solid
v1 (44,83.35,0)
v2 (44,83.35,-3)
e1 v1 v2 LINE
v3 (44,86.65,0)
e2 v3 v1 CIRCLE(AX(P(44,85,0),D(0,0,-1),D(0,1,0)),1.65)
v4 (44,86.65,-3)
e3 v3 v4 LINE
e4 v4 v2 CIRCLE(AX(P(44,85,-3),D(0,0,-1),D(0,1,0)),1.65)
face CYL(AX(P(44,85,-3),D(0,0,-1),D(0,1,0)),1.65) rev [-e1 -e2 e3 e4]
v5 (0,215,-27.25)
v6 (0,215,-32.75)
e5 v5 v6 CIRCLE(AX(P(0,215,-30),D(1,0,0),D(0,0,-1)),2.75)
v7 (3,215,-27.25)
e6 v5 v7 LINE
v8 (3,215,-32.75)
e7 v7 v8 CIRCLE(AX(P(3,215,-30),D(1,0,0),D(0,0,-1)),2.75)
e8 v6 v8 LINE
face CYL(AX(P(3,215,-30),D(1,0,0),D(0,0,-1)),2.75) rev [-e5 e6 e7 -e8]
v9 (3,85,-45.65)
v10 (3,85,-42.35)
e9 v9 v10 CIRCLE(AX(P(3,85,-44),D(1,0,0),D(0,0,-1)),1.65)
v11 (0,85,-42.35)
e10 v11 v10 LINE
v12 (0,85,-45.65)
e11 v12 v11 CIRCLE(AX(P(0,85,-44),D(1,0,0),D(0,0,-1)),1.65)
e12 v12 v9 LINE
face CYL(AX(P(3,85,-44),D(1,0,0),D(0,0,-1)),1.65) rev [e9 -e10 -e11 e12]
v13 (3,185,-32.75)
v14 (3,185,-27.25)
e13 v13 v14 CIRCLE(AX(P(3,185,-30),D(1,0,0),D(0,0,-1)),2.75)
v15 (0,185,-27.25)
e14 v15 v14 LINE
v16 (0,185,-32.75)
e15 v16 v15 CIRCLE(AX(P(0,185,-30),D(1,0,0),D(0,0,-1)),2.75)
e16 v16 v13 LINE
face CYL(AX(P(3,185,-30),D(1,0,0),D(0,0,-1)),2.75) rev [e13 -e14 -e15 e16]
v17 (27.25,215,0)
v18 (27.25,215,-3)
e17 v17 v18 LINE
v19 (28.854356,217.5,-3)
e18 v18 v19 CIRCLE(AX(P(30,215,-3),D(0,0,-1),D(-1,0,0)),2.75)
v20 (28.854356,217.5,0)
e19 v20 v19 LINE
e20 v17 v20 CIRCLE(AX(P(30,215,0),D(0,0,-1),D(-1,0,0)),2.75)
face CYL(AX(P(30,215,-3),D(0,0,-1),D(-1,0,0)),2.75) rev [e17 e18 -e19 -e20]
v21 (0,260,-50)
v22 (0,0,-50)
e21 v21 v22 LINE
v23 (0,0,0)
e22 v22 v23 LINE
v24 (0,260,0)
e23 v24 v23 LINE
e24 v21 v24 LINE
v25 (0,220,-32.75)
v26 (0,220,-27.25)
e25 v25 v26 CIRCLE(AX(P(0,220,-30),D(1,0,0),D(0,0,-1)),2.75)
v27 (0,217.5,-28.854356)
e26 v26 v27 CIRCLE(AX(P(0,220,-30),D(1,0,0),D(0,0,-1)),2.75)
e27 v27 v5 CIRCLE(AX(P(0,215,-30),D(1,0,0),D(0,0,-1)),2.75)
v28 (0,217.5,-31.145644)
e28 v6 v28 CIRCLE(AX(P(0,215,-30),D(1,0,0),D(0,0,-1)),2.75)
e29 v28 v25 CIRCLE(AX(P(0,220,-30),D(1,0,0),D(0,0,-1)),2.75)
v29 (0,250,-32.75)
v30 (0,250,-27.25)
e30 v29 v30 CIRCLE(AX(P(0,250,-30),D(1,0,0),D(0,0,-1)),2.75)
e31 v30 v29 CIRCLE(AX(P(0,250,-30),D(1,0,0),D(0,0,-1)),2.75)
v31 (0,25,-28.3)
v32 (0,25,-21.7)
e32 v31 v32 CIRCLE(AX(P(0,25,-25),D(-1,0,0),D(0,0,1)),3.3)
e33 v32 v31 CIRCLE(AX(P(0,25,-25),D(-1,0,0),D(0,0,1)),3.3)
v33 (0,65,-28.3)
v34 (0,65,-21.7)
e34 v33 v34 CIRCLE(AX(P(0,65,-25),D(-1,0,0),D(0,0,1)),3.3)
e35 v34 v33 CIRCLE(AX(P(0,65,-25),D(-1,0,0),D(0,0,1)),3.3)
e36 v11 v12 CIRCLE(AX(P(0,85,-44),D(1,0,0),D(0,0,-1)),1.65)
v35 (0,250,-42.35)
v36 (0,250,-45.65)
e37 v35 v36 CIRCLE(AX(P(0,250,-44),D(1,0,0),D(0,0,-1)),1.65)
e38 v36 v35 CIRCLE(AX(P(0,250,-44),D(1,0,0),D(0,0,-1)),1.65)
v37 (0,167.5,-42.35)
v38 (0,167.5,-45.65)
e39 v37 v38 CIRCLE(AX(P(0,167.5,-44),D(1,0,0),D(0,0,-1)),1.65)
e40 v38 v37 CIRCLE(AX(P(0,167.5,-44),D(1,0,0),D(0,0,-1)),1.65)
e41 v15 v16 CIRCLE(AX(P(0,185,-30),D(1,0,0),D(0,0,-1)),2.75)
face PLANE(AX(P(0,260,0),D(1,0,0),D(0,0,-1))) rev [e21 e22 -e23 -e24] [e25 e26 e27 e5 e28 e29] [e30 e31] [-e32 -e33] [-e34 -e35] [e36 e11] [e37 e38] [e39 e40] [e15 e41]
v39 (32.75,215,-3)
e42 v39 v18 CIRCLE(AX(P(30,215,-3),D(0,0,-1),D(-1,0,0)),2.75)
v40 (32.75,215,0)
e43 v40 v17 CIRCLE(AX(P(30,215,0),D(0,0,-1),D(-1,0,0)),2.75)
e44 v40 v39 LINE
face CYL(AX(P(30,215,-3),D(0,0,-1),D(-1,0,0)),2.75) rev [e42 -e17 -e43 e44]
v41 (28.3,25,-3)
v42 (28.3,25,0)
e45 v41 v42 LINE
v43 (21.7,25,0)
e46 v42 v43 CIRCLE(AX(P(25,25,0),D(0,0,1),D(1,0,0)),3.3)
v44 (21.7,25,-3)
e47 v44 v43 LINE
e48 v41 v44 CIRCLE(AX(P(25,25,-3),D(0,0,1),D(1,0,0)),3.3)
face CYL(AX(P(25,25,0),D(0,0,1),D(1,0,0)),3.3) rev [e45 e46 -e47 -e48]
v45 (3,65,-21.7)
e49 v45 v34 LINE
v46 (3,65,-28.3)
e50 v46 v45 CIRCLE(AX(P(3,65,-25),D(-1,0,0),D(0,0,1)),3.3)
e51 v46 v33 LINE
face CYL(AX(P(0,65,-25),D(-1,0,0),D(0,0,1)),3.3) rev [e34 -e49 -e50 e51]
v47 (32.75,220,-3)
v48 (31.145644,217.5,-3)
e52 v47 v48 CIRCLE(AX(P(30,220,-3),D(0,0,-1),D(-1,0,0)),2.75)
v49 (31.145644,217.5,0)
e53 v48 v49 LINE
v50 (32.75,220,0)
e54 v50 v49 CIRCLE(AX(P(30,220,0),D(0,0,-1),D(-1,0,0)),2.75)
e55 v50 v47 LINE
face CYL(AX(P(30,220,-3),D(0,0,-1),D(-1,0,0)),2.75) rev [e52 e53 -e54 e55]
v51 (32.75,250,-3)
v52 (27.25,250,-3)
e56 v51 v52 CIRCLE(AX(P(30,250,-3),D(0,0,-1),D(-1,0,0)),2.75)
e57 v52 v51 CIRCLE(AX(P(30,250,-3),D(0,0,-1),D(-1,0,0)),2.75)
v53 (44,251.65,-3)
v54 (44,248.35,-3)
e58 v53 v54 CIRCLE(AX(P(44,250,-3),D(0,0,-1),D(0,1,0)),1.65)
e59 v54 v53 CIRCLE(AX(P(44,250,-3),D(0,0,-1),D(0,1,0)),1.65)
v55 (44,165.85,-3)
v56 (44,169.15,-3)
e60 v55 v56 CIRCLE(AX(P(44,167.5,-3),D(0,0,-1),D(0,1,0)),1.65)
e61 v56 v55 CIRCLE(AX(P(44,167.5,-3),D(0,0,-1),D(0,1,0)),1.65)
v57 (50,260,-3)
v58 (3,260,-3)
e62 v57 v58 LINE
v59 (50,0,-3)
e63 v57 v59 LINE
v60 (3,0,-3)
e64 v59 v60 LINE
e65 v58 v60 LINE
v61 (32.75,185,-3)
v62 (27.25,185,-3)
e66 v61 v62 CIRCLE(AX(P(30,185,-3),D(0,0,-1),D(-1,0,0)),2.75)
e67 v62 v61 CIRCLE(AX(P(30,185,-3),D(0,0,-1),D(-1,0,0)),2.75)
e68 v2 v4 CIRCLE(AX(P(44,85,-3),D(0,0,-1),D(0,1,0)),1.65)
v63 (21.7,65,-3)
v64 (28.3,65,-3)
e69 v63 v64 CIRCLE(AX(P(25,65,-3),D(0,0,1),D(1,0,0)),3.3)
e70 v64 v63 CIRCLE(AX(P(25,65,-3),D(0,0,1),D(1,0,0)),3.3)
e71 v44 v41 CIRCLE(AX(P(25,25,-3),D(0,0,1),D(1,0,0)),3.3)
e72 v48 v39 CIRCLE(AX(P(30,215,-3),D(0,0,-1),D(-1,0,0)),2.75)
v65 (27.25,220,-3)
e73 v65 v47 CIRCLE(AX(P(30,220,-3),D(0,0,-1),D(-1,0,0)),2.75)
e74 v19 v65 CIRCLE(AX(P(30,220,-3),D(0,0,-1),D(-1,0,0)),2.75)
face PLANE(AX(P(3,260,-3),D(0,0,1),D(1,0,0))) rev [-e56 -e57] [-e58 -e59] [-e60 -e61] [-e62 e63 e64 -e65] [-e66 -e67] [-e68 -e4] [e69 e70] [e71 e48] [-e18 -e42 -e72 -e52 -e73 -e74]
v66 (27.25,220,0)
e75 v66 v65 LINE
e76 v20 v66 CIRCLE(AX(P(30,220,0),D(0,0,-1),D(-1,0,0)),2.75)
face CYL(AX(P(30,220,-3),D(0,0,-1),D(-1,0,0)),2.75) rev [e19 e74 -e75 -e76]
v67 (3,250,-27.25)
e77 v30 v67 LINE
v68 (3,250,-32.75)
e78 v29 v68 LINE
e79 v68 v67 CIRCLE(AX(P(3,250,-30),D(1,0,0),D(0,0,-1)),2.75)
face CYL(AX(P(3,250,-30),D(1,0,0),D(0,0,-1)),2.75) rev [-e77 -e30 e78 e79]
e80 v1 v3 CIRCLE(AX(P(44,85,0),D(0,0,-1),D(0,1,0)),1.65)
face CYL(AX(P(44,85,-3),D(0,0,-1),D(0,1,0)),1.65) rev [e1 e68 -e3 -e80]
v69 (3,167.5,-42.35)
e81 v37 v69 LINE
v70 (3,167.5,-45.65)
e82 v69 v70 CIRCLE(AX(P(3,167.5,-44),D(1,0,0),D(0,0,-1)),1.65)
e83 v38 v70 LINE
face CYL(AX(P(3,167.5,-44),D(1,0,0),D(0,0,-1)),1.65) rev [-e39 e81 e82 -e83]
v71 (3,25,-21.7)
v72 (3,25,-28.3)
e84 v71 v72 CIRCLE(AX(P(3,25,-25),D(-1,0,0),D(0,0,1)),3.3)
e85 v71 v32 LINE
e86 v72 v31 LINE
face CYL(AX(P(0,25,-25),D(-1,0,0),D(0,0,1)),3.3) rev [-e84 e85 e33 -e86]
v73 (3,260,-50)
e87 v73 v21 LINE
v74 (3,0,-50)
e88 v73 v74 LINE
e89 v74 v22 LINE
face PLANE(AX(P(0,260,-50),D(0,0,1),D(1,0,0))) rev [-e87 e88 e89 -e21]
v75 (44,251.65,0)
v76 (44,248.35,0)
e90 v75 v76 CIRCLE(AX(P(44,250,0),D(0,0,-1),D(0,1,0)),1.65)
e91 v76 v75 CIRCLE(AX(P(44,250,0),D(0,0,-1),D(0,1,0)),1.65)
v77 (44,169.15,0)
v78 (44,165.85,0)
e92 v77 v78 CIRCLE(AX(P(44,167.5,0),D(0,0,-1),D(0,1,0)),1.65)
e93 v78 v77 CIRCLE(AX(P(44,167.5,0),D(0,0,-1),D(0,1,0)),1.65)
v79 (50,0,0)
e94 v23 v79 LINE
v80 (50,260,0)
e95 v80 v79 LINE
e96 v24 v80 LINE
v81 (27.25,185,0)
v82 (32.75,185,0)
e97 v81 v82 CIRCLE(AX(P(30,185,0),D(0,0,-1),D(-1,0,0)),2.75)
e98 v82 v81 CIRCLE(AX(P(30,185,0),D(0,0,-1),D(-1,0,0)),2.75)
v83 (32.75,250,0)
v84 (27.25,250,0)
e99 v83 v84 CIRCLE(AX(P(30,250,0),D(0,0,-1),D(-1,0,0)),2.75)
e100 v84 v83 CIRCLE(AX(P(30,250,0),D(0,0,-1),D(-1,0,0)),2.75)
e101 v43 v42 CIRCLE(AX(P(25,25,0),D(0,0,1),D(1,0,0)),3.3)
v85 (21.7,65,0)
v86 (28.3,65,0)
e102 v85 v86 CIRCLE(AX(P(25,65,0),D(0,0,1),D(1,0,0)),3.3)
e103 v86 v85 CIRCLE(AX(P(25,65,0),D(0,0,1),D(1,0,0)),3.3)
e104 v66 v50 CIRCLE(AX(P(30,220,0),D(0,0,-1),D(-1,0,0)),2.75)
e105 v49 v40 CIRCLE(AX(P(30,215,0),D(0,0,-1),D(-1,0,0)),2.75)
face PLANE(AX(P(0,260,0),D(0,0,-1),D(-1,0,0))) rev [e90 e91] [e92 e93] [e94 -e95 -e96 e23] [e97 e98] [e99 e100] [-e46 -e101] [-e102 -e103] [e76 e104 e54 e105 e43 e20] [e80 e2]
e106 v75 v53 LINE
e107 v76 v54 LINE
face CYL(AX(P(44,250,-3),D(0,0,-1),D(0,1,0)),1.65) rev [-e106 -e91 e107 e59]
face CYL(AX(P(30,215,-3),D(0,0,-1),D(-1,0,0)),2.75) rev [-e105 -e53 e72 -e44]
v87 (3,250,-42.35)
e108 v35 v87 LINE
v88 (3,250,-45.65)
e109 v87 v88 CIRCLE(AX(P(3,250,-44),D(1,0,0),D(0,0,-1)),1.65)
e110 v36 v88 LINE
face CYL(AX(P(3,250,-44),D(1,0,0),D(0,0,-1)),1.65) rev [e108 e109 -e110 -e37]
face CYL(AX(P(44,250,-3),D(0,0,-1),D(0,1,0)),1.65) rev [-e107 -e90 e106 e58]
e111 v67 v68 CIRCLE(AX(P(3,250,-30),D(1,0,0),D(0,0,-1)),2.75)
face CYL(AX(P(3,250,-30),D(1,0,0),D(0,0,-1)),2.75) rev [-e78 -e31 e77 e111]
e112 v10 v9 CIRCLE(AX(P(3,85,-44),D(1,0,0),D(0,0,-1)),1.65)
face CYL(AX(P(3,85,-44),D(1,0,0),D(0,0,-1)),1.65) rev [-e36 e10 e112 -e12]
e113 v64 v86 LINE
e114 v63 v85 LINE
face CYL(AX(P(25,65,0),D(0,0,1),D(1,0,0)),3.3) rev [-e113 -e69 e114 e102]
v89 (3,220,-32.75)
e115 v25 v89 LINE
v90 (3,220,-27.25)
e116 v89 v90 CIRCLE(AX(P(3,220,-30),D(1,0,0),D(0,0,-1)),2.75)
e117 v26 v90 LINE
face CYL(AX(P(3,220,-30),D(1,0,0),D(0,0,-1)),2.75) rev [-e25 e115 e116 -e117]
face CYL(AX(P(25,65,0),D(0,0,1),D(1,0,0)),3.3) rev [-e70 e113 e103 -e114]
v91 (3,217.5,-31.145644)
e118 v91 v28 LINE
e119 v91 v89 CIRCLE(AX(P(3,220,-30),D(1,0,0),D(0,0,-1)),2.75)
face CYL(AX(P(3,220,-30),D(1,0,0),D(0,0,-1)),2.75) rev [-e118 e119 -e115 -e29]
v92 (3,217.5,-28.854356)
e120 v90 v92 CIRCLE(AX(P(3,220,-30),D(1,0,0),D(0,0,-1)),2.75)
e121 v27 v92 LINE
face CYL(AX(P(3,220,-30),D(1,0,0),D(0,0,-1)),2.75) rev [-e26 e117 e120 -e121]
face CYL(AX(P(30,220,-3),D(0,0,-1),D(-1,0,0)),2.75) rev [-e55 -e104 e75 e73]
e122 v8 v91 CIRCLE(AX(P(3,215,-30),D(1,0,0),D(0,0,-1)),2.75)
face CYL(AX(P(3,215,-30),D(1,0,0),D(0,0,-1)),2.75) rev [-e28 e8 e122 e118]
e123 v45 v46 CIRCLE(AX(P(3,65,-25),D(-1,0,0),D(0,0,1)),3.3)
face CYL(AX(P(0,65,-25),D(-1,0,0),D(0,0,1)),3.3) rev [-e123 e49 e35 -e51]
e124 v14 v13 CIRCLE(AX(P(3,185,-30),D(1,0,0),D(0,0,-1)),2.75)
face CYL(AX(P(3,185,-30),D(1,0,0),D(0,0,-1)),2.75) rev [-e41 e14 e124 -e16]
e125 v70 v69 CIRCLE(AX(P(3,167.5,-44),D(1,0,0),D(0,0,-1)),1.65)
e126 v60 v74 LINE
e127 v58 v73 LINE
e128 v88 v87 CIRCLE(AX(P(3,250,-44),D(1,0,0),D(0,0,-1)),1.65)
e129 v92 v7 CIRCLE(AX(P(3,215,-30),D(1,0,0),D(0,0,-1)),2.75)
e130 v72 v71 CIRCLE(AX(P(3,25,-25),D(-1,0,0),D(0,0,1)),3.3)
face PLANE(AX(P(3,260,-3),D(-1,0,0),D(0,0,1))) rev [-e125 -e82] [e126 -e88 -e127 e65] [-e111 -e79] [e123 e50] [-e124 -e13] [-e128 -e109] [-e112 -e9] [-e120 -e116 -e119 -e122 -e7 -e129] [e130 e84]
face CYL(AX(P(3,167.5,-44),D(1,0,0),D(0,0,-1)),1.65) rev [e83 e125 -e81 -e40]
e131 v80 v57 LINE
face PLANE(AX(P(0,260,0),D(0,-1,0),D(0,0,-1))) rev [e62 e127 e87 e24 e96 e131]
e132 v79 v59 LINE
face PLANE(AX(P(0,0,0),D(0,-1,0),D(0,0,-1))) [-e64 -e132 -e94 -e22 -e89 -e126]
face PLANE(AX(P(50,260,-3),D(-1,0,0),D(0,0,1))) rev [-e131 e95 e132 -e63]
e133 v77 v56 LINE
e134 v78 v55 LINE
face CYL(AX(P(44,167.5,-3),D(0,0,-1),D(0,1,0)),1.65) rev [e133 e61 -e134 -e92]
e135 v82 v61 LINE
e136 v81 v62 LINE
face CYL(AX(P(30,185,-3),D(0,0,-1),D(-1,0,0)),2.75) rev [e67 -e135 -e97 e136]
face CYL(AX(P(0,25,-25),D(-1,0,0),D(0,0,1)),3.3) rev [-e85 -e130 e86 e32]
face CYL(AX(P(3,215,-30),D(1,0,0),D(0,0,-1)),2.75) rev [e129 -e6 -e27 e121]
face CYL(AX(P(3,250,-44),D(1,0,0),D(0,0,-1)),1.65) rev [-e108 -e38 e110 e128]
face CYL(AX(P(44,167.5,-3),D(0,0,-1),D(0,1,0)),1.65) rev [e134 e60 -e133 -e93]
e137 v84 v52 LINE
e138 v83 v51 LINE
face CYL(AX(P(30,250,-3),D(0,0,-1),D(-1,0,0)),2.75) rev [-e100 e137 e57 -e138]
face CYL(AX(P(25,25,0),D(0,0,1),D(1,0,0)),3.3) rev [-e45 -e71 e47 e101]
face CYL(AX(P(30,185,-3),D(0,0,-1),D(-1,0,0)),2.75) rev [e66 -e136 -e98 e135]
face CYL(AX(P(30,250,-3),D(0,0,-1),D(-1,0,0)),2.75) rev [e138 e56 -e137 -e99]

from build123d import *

# Parameters (mm, degrees)
EXTRUDE_1_DEPTH    = 260
HOLE_WIZARD_M5_1_D = 5.5
HOLE_WIZARD_M5_2_D = 5.5
HOLE_WIZARD_M6_1_D = 6.6
HOLE_WIZARD_M6_2_D = 6.6
HOLE_WIZARD_M4_1_D = 3.3
HOLE_WIZARD_M4_2_D = 3.3


with BuildPart() as part:
    # 草图1 → 凸台-拉伸1 (new body)
    with BuildSketch(Plane(origin=(0, 0, 0), x_dir=(1, 0, 0), z_dir=(0, 1, 0))):
        Polygon((0, 0), (50, 0), (50, 3), (3, 3), (3, 50), (0, 50), align=None)
    extrude(amount=EXTRUDE_1_DEPTH)

    # M5 间隙孔1 (through all)
    with Locations(Plane(origin=(0, 0, -3), x_dir=(-1, 0, 0), z_dir=(0, 0, -1))):
        with Locations((-30, 250), (-30, 215), (-30, 220), (-30, 185)):
            Hole(HOLE_WIZARD_M5_1_D / 2)

    # M5 间隙孔2 (through all)
    with Locations(Plane(origin=(3, 0, 0), x_dir=(0, 0, -1), z_dir=(1, 0, 0))):
        with Locations((30, 220), (30, 185), (30, 250), (30, 215)):
            Hole(HOLE_WIZARD_M5_2_D / 2)

    # M6 间隙孔1 (through all)
    with Locations(Plane.XY):
        with Locations((25, 65), (25, 25)):
            Hole(HOLE_WIZARD_M6_1_D / 2)

    # M6 间隙孔2 (through all)
    with Locations(Plane.ZY):
        with Locations((-25, 65), (-25, 25)):
            Hole(HOLE_WIZARD_M6_2_D / 2)

    # M4 螺纹孔1 (through all)
    with Locations(Plane(origin=(0, 0, -3), x_dir=(-1, 0, 0), z_dir=(0, 0, -1))):
        with Locations((-44, 250), (-44, 167.5), (-44, 85)):
            Hole(HOLE_WIZARD_M4_1_D / 2)

    # M4 螺纹孔2 (through all)
    with Locations(Plane(origin=(3, 0, 0), x_dir=(0, 0, -1), z_dir=(1, 0, 0))):
        with Locations((44, 250), (44, 167.5), (44, 85)):
            Hole(HOLE_WIZARD_M4_2_D / 2)


solid = part.part
